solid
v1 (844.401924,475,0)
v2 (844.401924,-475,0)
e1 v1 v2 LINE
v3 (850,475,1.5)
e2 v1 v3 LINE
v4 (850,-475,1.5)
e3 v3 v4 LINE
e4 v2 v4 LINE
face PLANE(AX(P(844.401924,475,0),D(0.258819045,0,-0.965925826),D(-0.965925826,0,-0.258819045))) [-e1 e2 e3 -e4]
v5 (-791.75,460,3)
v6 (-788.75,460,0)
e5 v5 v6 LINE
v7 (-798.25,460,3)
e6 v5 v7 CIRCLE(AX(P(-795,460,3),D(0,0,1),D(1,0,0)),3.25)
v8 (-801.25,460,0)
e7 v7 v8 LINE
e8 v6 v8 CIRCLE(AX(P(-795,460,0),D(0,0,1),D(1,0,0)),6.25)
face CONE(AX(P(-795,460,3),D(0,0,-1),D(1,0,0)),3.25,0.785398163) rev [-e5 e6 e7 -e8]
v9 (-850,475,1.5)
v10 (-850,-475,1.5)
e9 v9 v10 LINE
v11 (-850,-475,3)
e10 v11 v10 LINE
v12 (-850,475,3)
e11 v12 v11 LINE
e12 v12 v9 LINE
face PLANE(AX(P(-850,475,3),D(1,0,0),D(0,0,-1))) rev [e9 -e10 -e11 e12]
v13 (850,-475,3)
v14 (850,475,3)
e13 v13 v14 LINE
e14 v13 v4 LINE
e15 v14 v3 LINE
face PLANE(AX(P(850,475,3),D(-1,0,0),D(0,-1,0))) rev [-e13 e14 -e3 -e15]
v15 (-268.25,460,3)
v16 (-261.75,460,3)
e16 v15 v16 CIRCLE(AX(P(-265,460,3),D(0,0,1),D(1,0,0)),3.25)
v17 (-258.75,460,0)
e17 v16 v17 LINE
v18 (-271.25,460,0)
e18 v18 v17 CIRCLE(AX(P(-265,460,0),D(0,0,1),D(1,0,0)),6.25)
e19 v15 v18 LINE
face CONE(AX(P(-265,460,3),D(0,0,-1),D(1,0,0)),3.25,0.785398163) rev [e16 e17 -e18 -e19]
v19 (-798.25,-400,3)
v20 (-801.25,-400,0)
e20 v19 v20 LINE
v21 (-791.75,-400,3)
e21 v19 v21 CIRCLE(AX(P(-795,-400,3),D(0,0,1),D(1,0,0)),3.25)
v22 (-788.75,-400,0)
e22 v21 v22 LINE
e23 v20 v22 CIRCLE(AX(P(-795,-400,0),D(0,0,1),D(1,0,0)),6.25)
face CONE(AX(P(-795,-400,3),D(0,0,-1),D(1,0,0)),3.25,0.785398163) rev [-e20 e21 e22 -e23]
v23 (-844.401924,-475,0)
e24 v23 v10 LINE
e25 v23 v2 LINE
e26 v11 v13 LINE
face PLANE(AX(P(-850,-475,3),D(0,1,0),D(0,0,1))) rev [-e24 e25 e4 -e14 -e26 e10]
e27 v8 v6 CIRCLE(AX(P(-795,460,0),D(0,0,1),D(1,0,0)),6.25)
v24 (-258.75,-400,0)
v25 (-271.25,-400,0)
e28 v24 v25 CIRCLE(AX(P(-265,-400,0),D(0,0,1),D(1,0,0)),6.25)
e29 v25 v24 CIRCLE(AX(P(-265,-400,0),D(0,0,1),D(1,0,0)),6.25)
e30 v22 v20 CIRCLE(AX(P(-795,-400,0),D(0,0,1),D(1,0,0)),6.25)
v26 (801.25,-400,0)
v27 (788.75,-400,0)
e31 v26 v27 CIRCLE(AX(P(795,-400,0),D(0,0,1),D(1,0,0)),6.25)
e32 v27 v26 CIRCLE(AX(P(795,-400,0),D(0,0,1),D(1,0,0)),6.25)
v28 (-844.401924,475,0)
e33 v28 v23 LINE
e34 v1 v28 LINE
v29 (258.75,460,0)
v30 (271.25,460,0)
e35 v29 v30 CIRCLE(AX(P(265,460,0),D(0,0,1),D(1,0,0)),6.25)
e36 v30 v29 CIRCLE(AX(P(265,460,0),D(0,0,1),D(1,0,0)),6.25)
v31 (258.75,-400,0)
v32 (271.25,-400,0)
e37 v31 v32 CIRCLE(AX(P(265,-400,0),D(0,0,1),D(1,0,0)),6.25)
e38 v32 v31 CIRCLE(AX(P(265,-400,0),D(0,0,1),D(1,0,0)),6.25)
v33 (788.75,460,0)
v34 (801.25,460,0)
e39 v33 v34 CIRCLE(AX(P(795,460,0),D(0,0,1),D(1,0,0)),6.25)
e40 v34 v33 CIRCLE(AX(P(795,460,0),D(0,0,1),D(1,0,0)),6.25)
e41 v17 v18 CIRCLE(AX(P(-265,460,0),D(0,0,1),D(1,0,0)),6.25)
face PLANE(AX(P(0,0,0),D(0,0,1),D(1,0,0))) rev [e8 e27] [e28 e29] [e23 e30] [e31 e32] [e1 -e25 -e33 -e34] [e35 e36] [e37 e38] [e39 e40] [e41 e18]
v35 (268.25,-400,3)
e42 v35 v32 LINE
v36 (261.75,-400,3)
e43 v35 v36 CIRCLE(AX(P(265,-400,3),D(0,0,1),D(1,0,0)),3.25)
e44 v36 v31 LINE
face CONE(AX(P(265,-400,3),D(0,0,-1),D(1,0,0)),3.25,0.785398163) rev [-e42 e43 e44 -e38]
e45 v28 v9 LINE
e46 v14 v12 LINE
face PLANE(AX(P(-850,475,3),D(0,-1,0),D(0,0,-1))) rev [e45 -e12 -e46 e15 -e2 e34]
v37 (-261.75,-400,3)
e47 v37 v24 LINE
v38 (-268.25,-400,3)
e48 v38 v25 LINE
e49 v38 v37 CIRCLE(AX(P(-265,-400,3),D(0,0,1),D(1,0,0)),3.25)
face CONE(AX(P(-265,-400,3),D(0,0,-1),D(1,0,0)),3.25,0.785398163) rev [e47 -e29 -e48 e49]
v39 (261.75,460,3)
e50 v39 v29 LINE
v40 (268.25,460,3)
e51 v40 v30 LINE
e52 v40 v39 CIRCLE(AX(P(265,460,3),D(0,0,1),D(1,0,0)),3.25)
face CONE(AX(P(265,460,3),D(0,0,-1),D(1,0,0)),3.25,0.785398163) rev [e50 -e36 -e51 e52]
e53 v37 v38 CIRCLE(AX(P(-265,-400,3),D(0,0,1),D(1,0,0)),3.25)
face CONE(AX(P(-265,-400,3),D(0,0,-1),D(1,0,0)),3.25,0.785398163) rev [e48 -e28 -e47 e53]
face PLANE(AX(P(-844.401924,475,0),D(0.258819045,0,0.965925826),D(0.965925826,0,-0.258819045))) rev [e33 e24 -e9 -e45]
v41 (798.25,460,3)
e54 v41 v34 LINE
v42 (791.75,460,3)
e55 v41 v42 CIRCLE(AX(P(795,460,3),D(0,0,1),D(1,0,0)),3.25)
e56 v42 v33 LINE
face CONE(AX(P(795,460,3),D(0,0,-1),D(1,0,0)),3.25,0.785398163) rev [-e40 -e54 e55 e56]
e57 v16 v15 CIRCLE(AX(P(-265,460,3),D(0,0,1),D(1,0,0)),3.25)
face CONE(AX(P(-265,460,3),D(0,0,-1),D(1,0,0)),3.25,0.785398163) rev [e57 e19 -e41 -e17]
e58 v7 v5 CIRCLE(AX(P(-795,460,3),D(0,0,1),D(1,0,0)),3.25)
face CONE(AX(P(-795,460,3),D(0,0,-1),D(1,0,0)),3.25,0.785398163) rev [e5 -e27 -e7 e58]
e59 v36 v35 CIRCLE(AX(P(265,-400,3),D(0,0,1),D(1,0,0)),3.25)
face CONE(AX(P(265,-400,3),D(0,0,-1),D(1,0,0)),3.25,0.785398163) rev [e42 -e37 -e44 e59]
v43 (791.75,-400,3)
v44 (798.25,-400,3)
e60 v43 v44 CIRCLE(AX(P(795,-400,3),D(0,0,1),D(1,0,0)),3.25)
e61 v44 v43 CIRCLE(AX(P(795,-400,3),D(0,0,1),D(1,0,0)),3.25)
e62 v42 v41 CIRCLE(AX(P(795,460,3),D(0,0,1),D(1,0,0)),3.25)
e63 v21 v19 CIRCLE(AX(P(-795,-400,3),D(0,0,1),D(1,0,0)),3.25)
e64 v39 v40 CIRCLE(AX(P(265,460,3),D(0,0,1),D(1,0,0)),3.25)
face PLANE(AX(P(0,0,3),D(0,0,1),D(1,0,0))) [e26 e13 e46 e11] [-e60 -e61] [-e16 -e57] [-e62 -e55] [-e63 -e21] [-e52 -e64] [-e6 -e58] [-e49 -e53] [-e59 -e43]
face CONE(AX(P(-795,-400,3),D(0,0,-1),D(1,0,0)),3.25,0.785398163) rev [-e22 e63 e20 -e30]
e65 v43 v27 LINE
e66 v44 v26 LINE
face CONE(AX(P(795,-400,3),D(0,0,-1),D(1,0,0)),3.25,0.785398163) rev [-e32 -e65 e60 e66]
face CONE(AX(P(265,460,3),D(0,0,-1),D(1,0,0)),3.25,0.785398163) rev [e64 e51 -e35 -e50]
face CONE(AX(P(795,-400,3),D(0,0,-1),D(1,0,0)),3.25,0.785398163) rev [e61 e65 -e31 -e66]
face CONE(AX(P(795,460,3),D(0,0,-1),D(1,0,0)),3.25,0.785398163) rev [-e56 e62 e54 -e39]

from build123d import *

# Parameters (mm, degrees)
SKETCH_1_W                    = 1700
SKETCH_1_H                    = 950
EXTRUDE_1_DEPTH               = 3
SKETCH_2_R                    = 3.25
CUT_EXTRUDE_1_DEPTH           = 3
CUT_EXTRUDE_1_DRAFT           = 45
CUT_EXTRUDE_1_PROFILE_2_DEPTH = 3
CUT_EXTRUDE_1_PROFILE_2_DRAFT = 45
CUT_EXTRUDE_1_PROFILE_3_DEPTH = 3
CUT_EXTRUDE_1_PROFILE_3_DRAFT = 45
CUT_EXTRUDE_1_PROFILE_4_DEPTH = 3
CUT_EXTRUDE_1_PROFILE_4_DRAFT = 45
CUT_EXTRUDE_1_PROFILE_5_DEPTH = 3
CUT_EXTRUDE_1_PROFILE_5_DRAFT = 45
CUT_EXTRUDE_1_PROFILE_6_DEPTH = 3
CUT_EXTRUDE_1_PROFILE_6_DRAFT = 45
CUT_EXTRUDE_1_PROFILE_7_DEPTH = 3
CUT_EXTRUDE_1_PROFILE_7_DRAFT = 45
CUT_EXTRUDE_1_PROFILE_8_DEPTH = 3
CUT_EXTRUDE_1_PROFILE_8_DRAFT = 45
CUT_EXTRUDE_2_DEPTH           = 1275.758408484


with BuildPart() as part:
    # 草图1 → 凸台-拉伸1 (new body)
    with BuildSketch(Plane.XY):
        Rectangle(SKETCH_1_W, SKETCH_1_H)
    extrude(amount=EXTRUDE_1_DEPTH)


with BuildPart() as cut_extrude_1_tool:
    # 草图2 → 切除-拉伸1 (with draft: the straight prism first)
    with BuildSketch(Plane.XY.offset(3)):
        with Locations((-795, 460)):
            Circle(SKETCH_2_R)
    extrude(amount=-CUT_EXTRUDE_1_DEPTH)
    # 切除-拉伸1: the draft: its side faces are tilted about the plane it starts from
    cut_extrude_1_sides = [cut_extrude_1_tool.faces().sort_by_distance(p)[0] for p in [
        (-798.25, 460, 1.5),
    ]]
    draft(cut_extrude_1_sides, Plane.XY.offset(3), CUT_EXTRUDE_1_DRAFT)


with BuildPart() as part_1:
    add(part.part)

    # 切除-拉伸1: cut by cut_extrude_1_tool
    add(cut_extrude_1_tool.part, mode=Mode.SUBTRACT)


with BuildPart() as cut_extrude_1_profile_2_tool:
    # 草图2 → 切除-拉伸1 profile 2 (with draft: the straight prism first)
    with BuildSketch(Plane.XY.offset(3)):
        with Locations((-265, 460)):
            Circle(SKETCH_2_R)
    extrude(amount=-CUT_EXTRUDE_1_PROFILE_2_DEPTH)
    # 切除-拉伸1 profile 2: the draft: its side faces are tilted about the plane it starts from
    cut_extrude_1_profile_2_sides = [cut_extrude_1_profile_2_tool.faces().sort_by_distance(p)[0] for p in [
        (-268.25, 460, 1.5),
    ]]
    draft(cut_extrude_1_profile_2_sides, Plane.XY.offset(3), CUT_EXTRUDE_1_PROFILE_2_DRAFT)


with BuildPart() as part_2:
    add(part_1.part)

    # 切除-拉伸1 profile 2: cut by cut_extrude_1_profile_2_tool
    add(cut_extrude_1_profile_2_tool.part, mode=Mode.SUBTRACT)


with BuildPart() as cut_extrude_1_profile_3_tool:
    # 草图2 → 切除-拉伸1 profile 3 (with draft: the straight prism first)
    with BuildSketch(Plane.XY.offset(3)):
        with Locations((265, 460)):
            Circle(SKETCH_2_R)
    extrude(amount=-CUT_EXTRUDE_1_PROFILE_3_DEPTH)
    # 切除-拉伸1 profile 3: the draft: its side faces are tilted about the plane it starts from
    cut_extrude_1_profile_3_sides = [cut_extrude_1_profile_3_tool.faces().sort_by_distance(p)[0] for p in [
        (261.75, 460, 1.5),
    ]]
    draft(cut_extrude_1_profile_3_sides, Plane.XY.offset(3), CUT_EXTRUDE_1_PROFILE_3_DRAFT)


with BuildPart() as part_3:
    add(part_2.part)

    # 切除-拉伸1 profile 3: cut by cut_extrude_1_profile_3_tool
    add(cut_extrude_1_profile_3_tool.part, mode=Mode.SUBTRACT)


with BuildPart() as cut_extrude_1_profile_4_tool:
    # 草图2 → 切除-拉伸1 profile 4 (with draft: the straight prism first)
    with BuildSketch(Plane.XY.offset(3)):
        with Locations((795, 460)):
            Circle(SKETCH_2_R)
    extrude(amount=-CUT_EXTRUDE_1_PROFILE_4_DEPTH)
    # 切除-拉伸1 profile 4: the draft: its side faces are tilted about the plane it starts from
    cut_extrude_1_profile_4_sides = [cut_extrude_1_profile_4_tool.faces().sort_by_distance(p)[0] for p in [
        (791.75, 460, 1.5),
    ]]
    draft(cut_extrude_1_profile_4_sides, Plane.XY.offset(3), CUT_EXTRUDE_1_PROFILE_4_DRAFT)


with BuildPart() as part_4:
    add(part_3.part)

    # 切除-拉伸1 profile 4: cut by cut_extrude_1_profile_4_tool
    add(cut_extrude_1_profile_4_tool.part, mode=Mode.SUBTRACT)


with BuildPart() as cut_extrude_1_profile_5_tool:
    # 草图2 → 切除-拉伸1 profile 5 (with draft: the straight prism first)
    with BuildSketch(Plane.XY.offset(3)):
        with Locations((795, -400)):
            Circle(SKETCH_2_R)
    extrude(amount=-CUT_EXTRUDE_1_PROFILE_5_DEPTH)
    # 切除-拉伸1 profile 5: the draft: its side faces are tilted about the plane it starts from
    cut_extrude_1_profile_5_sides = [cut_extrude_1_profile_5_tool.faces().sort_by_distance(p)[0] for p in [
        (791.75, -400, 1.5),
    ]]
    draft(cut_extrude_1_profile_5_sides, Plane.XY.offset(3), CUT_EXTRUDE_1_PROFILE_5_DRAFT)


with BuildPart() as part_5:
    add(part_4.part)

    # 切除-拉伸1 profile 5: cut by cut_extrude_1_profile_5_tool
    add(cut_extrude_1_profile_5_tool.part, mode=Mode.SUBTRACT)


with BuildPart() as cut_extrude_1_profile_6_tool:
    # 草图2 → 切除-拉伸1 profile 6 (with draft: the straight prism first)
    with BuildSketch(Plane.XY.offset(3)):
        with Locations((265, -400)):
            Circle(SKETCH_2_R)
    extrude(amount=-CUT_EXTRUDE_1_PROFILE_6_DEPTH)
    # 切除-拉伸1 profile 6: the draft: its side faces are tilted about the plane it starts from
    cut_extrude_1_profile_6_sides = [cut_extrude_1_profile_6_tool.faces().sort_by_distance(p)[0] for p in [
        (261.75, -400, 1.5),
    ]]
    draft(cut_extrude_1_profile_6_sides, Plane.XY.offset(3), CUT_EXTRUDE_1_PROFILE_6_DRAFT)


with BuildPart() as part_6:
    add(part_5.part)

    # 切除-拉伸1 profile 6: cut by cut_extrude_1_profile_6_tool
    add(cut_extrude_1_profile_6_tool.part, mode=Mode.SUBTRACT)


with BuildPart() as cut_extrude_1_profile_7_tool:
    # 草图2 → 切除-拉伸1 profile 7 (with draft: the straight prism first)
    with BuildSketch(Plane.XY.offset(3)):
        with Locations((-265, -400)):
            Circle(SKETCH_2_R)
    extrude(amount=-CUT_EXTRUDE_1_PROFILE_7_DEPTH)
    # 切除-拉伸1 profile 7: the draft: its side faces are tilted about the plane it starts from
    cut_extrude_1_profile_7_sides = [cut_extrude_1_profile_7_tool.faces().sort_by_distance(p)[0] for p in [
        (-268.25, -400, 1.5),
    ]]
    draft(cut_extrude_1_profile_7_sides, Plane.XY.offset(3), CUT_EXTRUDE_1_PROFILE_7_DRAFT)


with BuildPart() as part_7:
    add(part_6.part)

    # 切除-拉伸1 profile 7: cut by cut_extrude_1_profile_7_tool
    add(cut_extrude_1_profile_7_tool.part, mode=Mode.SUBTRACT)


with BuildPart() as cut_extrude_1_profile_8_tool:
    # 草图2 → 切除-拉伸1 profile 8 (with draft: the straight prism first)
    with BuildSketch(Plane.XY.offset(3)):
        with Locations((-795, -400)):
            Circle(SKETCH_2_R)
    extrude(amount=-CUT_EXTRUDE_1_PROFILE_8_DEPTH)
    # 切除-拉伸1 profile 8: the draft: its side faces are tilted about the plane it starts from
    cut_extrude_1_profile_8_sides = [cut_extrude_1_profile_8_tool.faces().sort_by_distance(p)[0] for p in [
        (-798.25, -400, 1.5),
    ]]
    draft(cut_extrude_1_profile_8_sides, Plane.XY.offset(3), CUT_EXTRUDE_1_PROFILE_8_DRAFT)


with BuildPart() as part_8:
    add(part_7.part)

    # 切除-拉伸1 profile 8: cut by cut_extrude_1_profile_8_tool
    add(cut_extrude_1_profile_8_tool.part, mode=Mode.SUBTRACT)

    # 草图3 → 切除-拉伸2 (cut, through all)
    with BuildSketch(Plane.XZ.offset(475)):
        Polygon((844.401923789, 0), (850, 1.5), (850, 0), align=None)
        Polygon((-850, 1.5), (-850, 0), (-844.401923789, 0), align=None)
    extrude(amount=-CUT_EXTRUDE_2_DEPTH, mode=Mode.SUBTRACT)


solid = part_8.part
